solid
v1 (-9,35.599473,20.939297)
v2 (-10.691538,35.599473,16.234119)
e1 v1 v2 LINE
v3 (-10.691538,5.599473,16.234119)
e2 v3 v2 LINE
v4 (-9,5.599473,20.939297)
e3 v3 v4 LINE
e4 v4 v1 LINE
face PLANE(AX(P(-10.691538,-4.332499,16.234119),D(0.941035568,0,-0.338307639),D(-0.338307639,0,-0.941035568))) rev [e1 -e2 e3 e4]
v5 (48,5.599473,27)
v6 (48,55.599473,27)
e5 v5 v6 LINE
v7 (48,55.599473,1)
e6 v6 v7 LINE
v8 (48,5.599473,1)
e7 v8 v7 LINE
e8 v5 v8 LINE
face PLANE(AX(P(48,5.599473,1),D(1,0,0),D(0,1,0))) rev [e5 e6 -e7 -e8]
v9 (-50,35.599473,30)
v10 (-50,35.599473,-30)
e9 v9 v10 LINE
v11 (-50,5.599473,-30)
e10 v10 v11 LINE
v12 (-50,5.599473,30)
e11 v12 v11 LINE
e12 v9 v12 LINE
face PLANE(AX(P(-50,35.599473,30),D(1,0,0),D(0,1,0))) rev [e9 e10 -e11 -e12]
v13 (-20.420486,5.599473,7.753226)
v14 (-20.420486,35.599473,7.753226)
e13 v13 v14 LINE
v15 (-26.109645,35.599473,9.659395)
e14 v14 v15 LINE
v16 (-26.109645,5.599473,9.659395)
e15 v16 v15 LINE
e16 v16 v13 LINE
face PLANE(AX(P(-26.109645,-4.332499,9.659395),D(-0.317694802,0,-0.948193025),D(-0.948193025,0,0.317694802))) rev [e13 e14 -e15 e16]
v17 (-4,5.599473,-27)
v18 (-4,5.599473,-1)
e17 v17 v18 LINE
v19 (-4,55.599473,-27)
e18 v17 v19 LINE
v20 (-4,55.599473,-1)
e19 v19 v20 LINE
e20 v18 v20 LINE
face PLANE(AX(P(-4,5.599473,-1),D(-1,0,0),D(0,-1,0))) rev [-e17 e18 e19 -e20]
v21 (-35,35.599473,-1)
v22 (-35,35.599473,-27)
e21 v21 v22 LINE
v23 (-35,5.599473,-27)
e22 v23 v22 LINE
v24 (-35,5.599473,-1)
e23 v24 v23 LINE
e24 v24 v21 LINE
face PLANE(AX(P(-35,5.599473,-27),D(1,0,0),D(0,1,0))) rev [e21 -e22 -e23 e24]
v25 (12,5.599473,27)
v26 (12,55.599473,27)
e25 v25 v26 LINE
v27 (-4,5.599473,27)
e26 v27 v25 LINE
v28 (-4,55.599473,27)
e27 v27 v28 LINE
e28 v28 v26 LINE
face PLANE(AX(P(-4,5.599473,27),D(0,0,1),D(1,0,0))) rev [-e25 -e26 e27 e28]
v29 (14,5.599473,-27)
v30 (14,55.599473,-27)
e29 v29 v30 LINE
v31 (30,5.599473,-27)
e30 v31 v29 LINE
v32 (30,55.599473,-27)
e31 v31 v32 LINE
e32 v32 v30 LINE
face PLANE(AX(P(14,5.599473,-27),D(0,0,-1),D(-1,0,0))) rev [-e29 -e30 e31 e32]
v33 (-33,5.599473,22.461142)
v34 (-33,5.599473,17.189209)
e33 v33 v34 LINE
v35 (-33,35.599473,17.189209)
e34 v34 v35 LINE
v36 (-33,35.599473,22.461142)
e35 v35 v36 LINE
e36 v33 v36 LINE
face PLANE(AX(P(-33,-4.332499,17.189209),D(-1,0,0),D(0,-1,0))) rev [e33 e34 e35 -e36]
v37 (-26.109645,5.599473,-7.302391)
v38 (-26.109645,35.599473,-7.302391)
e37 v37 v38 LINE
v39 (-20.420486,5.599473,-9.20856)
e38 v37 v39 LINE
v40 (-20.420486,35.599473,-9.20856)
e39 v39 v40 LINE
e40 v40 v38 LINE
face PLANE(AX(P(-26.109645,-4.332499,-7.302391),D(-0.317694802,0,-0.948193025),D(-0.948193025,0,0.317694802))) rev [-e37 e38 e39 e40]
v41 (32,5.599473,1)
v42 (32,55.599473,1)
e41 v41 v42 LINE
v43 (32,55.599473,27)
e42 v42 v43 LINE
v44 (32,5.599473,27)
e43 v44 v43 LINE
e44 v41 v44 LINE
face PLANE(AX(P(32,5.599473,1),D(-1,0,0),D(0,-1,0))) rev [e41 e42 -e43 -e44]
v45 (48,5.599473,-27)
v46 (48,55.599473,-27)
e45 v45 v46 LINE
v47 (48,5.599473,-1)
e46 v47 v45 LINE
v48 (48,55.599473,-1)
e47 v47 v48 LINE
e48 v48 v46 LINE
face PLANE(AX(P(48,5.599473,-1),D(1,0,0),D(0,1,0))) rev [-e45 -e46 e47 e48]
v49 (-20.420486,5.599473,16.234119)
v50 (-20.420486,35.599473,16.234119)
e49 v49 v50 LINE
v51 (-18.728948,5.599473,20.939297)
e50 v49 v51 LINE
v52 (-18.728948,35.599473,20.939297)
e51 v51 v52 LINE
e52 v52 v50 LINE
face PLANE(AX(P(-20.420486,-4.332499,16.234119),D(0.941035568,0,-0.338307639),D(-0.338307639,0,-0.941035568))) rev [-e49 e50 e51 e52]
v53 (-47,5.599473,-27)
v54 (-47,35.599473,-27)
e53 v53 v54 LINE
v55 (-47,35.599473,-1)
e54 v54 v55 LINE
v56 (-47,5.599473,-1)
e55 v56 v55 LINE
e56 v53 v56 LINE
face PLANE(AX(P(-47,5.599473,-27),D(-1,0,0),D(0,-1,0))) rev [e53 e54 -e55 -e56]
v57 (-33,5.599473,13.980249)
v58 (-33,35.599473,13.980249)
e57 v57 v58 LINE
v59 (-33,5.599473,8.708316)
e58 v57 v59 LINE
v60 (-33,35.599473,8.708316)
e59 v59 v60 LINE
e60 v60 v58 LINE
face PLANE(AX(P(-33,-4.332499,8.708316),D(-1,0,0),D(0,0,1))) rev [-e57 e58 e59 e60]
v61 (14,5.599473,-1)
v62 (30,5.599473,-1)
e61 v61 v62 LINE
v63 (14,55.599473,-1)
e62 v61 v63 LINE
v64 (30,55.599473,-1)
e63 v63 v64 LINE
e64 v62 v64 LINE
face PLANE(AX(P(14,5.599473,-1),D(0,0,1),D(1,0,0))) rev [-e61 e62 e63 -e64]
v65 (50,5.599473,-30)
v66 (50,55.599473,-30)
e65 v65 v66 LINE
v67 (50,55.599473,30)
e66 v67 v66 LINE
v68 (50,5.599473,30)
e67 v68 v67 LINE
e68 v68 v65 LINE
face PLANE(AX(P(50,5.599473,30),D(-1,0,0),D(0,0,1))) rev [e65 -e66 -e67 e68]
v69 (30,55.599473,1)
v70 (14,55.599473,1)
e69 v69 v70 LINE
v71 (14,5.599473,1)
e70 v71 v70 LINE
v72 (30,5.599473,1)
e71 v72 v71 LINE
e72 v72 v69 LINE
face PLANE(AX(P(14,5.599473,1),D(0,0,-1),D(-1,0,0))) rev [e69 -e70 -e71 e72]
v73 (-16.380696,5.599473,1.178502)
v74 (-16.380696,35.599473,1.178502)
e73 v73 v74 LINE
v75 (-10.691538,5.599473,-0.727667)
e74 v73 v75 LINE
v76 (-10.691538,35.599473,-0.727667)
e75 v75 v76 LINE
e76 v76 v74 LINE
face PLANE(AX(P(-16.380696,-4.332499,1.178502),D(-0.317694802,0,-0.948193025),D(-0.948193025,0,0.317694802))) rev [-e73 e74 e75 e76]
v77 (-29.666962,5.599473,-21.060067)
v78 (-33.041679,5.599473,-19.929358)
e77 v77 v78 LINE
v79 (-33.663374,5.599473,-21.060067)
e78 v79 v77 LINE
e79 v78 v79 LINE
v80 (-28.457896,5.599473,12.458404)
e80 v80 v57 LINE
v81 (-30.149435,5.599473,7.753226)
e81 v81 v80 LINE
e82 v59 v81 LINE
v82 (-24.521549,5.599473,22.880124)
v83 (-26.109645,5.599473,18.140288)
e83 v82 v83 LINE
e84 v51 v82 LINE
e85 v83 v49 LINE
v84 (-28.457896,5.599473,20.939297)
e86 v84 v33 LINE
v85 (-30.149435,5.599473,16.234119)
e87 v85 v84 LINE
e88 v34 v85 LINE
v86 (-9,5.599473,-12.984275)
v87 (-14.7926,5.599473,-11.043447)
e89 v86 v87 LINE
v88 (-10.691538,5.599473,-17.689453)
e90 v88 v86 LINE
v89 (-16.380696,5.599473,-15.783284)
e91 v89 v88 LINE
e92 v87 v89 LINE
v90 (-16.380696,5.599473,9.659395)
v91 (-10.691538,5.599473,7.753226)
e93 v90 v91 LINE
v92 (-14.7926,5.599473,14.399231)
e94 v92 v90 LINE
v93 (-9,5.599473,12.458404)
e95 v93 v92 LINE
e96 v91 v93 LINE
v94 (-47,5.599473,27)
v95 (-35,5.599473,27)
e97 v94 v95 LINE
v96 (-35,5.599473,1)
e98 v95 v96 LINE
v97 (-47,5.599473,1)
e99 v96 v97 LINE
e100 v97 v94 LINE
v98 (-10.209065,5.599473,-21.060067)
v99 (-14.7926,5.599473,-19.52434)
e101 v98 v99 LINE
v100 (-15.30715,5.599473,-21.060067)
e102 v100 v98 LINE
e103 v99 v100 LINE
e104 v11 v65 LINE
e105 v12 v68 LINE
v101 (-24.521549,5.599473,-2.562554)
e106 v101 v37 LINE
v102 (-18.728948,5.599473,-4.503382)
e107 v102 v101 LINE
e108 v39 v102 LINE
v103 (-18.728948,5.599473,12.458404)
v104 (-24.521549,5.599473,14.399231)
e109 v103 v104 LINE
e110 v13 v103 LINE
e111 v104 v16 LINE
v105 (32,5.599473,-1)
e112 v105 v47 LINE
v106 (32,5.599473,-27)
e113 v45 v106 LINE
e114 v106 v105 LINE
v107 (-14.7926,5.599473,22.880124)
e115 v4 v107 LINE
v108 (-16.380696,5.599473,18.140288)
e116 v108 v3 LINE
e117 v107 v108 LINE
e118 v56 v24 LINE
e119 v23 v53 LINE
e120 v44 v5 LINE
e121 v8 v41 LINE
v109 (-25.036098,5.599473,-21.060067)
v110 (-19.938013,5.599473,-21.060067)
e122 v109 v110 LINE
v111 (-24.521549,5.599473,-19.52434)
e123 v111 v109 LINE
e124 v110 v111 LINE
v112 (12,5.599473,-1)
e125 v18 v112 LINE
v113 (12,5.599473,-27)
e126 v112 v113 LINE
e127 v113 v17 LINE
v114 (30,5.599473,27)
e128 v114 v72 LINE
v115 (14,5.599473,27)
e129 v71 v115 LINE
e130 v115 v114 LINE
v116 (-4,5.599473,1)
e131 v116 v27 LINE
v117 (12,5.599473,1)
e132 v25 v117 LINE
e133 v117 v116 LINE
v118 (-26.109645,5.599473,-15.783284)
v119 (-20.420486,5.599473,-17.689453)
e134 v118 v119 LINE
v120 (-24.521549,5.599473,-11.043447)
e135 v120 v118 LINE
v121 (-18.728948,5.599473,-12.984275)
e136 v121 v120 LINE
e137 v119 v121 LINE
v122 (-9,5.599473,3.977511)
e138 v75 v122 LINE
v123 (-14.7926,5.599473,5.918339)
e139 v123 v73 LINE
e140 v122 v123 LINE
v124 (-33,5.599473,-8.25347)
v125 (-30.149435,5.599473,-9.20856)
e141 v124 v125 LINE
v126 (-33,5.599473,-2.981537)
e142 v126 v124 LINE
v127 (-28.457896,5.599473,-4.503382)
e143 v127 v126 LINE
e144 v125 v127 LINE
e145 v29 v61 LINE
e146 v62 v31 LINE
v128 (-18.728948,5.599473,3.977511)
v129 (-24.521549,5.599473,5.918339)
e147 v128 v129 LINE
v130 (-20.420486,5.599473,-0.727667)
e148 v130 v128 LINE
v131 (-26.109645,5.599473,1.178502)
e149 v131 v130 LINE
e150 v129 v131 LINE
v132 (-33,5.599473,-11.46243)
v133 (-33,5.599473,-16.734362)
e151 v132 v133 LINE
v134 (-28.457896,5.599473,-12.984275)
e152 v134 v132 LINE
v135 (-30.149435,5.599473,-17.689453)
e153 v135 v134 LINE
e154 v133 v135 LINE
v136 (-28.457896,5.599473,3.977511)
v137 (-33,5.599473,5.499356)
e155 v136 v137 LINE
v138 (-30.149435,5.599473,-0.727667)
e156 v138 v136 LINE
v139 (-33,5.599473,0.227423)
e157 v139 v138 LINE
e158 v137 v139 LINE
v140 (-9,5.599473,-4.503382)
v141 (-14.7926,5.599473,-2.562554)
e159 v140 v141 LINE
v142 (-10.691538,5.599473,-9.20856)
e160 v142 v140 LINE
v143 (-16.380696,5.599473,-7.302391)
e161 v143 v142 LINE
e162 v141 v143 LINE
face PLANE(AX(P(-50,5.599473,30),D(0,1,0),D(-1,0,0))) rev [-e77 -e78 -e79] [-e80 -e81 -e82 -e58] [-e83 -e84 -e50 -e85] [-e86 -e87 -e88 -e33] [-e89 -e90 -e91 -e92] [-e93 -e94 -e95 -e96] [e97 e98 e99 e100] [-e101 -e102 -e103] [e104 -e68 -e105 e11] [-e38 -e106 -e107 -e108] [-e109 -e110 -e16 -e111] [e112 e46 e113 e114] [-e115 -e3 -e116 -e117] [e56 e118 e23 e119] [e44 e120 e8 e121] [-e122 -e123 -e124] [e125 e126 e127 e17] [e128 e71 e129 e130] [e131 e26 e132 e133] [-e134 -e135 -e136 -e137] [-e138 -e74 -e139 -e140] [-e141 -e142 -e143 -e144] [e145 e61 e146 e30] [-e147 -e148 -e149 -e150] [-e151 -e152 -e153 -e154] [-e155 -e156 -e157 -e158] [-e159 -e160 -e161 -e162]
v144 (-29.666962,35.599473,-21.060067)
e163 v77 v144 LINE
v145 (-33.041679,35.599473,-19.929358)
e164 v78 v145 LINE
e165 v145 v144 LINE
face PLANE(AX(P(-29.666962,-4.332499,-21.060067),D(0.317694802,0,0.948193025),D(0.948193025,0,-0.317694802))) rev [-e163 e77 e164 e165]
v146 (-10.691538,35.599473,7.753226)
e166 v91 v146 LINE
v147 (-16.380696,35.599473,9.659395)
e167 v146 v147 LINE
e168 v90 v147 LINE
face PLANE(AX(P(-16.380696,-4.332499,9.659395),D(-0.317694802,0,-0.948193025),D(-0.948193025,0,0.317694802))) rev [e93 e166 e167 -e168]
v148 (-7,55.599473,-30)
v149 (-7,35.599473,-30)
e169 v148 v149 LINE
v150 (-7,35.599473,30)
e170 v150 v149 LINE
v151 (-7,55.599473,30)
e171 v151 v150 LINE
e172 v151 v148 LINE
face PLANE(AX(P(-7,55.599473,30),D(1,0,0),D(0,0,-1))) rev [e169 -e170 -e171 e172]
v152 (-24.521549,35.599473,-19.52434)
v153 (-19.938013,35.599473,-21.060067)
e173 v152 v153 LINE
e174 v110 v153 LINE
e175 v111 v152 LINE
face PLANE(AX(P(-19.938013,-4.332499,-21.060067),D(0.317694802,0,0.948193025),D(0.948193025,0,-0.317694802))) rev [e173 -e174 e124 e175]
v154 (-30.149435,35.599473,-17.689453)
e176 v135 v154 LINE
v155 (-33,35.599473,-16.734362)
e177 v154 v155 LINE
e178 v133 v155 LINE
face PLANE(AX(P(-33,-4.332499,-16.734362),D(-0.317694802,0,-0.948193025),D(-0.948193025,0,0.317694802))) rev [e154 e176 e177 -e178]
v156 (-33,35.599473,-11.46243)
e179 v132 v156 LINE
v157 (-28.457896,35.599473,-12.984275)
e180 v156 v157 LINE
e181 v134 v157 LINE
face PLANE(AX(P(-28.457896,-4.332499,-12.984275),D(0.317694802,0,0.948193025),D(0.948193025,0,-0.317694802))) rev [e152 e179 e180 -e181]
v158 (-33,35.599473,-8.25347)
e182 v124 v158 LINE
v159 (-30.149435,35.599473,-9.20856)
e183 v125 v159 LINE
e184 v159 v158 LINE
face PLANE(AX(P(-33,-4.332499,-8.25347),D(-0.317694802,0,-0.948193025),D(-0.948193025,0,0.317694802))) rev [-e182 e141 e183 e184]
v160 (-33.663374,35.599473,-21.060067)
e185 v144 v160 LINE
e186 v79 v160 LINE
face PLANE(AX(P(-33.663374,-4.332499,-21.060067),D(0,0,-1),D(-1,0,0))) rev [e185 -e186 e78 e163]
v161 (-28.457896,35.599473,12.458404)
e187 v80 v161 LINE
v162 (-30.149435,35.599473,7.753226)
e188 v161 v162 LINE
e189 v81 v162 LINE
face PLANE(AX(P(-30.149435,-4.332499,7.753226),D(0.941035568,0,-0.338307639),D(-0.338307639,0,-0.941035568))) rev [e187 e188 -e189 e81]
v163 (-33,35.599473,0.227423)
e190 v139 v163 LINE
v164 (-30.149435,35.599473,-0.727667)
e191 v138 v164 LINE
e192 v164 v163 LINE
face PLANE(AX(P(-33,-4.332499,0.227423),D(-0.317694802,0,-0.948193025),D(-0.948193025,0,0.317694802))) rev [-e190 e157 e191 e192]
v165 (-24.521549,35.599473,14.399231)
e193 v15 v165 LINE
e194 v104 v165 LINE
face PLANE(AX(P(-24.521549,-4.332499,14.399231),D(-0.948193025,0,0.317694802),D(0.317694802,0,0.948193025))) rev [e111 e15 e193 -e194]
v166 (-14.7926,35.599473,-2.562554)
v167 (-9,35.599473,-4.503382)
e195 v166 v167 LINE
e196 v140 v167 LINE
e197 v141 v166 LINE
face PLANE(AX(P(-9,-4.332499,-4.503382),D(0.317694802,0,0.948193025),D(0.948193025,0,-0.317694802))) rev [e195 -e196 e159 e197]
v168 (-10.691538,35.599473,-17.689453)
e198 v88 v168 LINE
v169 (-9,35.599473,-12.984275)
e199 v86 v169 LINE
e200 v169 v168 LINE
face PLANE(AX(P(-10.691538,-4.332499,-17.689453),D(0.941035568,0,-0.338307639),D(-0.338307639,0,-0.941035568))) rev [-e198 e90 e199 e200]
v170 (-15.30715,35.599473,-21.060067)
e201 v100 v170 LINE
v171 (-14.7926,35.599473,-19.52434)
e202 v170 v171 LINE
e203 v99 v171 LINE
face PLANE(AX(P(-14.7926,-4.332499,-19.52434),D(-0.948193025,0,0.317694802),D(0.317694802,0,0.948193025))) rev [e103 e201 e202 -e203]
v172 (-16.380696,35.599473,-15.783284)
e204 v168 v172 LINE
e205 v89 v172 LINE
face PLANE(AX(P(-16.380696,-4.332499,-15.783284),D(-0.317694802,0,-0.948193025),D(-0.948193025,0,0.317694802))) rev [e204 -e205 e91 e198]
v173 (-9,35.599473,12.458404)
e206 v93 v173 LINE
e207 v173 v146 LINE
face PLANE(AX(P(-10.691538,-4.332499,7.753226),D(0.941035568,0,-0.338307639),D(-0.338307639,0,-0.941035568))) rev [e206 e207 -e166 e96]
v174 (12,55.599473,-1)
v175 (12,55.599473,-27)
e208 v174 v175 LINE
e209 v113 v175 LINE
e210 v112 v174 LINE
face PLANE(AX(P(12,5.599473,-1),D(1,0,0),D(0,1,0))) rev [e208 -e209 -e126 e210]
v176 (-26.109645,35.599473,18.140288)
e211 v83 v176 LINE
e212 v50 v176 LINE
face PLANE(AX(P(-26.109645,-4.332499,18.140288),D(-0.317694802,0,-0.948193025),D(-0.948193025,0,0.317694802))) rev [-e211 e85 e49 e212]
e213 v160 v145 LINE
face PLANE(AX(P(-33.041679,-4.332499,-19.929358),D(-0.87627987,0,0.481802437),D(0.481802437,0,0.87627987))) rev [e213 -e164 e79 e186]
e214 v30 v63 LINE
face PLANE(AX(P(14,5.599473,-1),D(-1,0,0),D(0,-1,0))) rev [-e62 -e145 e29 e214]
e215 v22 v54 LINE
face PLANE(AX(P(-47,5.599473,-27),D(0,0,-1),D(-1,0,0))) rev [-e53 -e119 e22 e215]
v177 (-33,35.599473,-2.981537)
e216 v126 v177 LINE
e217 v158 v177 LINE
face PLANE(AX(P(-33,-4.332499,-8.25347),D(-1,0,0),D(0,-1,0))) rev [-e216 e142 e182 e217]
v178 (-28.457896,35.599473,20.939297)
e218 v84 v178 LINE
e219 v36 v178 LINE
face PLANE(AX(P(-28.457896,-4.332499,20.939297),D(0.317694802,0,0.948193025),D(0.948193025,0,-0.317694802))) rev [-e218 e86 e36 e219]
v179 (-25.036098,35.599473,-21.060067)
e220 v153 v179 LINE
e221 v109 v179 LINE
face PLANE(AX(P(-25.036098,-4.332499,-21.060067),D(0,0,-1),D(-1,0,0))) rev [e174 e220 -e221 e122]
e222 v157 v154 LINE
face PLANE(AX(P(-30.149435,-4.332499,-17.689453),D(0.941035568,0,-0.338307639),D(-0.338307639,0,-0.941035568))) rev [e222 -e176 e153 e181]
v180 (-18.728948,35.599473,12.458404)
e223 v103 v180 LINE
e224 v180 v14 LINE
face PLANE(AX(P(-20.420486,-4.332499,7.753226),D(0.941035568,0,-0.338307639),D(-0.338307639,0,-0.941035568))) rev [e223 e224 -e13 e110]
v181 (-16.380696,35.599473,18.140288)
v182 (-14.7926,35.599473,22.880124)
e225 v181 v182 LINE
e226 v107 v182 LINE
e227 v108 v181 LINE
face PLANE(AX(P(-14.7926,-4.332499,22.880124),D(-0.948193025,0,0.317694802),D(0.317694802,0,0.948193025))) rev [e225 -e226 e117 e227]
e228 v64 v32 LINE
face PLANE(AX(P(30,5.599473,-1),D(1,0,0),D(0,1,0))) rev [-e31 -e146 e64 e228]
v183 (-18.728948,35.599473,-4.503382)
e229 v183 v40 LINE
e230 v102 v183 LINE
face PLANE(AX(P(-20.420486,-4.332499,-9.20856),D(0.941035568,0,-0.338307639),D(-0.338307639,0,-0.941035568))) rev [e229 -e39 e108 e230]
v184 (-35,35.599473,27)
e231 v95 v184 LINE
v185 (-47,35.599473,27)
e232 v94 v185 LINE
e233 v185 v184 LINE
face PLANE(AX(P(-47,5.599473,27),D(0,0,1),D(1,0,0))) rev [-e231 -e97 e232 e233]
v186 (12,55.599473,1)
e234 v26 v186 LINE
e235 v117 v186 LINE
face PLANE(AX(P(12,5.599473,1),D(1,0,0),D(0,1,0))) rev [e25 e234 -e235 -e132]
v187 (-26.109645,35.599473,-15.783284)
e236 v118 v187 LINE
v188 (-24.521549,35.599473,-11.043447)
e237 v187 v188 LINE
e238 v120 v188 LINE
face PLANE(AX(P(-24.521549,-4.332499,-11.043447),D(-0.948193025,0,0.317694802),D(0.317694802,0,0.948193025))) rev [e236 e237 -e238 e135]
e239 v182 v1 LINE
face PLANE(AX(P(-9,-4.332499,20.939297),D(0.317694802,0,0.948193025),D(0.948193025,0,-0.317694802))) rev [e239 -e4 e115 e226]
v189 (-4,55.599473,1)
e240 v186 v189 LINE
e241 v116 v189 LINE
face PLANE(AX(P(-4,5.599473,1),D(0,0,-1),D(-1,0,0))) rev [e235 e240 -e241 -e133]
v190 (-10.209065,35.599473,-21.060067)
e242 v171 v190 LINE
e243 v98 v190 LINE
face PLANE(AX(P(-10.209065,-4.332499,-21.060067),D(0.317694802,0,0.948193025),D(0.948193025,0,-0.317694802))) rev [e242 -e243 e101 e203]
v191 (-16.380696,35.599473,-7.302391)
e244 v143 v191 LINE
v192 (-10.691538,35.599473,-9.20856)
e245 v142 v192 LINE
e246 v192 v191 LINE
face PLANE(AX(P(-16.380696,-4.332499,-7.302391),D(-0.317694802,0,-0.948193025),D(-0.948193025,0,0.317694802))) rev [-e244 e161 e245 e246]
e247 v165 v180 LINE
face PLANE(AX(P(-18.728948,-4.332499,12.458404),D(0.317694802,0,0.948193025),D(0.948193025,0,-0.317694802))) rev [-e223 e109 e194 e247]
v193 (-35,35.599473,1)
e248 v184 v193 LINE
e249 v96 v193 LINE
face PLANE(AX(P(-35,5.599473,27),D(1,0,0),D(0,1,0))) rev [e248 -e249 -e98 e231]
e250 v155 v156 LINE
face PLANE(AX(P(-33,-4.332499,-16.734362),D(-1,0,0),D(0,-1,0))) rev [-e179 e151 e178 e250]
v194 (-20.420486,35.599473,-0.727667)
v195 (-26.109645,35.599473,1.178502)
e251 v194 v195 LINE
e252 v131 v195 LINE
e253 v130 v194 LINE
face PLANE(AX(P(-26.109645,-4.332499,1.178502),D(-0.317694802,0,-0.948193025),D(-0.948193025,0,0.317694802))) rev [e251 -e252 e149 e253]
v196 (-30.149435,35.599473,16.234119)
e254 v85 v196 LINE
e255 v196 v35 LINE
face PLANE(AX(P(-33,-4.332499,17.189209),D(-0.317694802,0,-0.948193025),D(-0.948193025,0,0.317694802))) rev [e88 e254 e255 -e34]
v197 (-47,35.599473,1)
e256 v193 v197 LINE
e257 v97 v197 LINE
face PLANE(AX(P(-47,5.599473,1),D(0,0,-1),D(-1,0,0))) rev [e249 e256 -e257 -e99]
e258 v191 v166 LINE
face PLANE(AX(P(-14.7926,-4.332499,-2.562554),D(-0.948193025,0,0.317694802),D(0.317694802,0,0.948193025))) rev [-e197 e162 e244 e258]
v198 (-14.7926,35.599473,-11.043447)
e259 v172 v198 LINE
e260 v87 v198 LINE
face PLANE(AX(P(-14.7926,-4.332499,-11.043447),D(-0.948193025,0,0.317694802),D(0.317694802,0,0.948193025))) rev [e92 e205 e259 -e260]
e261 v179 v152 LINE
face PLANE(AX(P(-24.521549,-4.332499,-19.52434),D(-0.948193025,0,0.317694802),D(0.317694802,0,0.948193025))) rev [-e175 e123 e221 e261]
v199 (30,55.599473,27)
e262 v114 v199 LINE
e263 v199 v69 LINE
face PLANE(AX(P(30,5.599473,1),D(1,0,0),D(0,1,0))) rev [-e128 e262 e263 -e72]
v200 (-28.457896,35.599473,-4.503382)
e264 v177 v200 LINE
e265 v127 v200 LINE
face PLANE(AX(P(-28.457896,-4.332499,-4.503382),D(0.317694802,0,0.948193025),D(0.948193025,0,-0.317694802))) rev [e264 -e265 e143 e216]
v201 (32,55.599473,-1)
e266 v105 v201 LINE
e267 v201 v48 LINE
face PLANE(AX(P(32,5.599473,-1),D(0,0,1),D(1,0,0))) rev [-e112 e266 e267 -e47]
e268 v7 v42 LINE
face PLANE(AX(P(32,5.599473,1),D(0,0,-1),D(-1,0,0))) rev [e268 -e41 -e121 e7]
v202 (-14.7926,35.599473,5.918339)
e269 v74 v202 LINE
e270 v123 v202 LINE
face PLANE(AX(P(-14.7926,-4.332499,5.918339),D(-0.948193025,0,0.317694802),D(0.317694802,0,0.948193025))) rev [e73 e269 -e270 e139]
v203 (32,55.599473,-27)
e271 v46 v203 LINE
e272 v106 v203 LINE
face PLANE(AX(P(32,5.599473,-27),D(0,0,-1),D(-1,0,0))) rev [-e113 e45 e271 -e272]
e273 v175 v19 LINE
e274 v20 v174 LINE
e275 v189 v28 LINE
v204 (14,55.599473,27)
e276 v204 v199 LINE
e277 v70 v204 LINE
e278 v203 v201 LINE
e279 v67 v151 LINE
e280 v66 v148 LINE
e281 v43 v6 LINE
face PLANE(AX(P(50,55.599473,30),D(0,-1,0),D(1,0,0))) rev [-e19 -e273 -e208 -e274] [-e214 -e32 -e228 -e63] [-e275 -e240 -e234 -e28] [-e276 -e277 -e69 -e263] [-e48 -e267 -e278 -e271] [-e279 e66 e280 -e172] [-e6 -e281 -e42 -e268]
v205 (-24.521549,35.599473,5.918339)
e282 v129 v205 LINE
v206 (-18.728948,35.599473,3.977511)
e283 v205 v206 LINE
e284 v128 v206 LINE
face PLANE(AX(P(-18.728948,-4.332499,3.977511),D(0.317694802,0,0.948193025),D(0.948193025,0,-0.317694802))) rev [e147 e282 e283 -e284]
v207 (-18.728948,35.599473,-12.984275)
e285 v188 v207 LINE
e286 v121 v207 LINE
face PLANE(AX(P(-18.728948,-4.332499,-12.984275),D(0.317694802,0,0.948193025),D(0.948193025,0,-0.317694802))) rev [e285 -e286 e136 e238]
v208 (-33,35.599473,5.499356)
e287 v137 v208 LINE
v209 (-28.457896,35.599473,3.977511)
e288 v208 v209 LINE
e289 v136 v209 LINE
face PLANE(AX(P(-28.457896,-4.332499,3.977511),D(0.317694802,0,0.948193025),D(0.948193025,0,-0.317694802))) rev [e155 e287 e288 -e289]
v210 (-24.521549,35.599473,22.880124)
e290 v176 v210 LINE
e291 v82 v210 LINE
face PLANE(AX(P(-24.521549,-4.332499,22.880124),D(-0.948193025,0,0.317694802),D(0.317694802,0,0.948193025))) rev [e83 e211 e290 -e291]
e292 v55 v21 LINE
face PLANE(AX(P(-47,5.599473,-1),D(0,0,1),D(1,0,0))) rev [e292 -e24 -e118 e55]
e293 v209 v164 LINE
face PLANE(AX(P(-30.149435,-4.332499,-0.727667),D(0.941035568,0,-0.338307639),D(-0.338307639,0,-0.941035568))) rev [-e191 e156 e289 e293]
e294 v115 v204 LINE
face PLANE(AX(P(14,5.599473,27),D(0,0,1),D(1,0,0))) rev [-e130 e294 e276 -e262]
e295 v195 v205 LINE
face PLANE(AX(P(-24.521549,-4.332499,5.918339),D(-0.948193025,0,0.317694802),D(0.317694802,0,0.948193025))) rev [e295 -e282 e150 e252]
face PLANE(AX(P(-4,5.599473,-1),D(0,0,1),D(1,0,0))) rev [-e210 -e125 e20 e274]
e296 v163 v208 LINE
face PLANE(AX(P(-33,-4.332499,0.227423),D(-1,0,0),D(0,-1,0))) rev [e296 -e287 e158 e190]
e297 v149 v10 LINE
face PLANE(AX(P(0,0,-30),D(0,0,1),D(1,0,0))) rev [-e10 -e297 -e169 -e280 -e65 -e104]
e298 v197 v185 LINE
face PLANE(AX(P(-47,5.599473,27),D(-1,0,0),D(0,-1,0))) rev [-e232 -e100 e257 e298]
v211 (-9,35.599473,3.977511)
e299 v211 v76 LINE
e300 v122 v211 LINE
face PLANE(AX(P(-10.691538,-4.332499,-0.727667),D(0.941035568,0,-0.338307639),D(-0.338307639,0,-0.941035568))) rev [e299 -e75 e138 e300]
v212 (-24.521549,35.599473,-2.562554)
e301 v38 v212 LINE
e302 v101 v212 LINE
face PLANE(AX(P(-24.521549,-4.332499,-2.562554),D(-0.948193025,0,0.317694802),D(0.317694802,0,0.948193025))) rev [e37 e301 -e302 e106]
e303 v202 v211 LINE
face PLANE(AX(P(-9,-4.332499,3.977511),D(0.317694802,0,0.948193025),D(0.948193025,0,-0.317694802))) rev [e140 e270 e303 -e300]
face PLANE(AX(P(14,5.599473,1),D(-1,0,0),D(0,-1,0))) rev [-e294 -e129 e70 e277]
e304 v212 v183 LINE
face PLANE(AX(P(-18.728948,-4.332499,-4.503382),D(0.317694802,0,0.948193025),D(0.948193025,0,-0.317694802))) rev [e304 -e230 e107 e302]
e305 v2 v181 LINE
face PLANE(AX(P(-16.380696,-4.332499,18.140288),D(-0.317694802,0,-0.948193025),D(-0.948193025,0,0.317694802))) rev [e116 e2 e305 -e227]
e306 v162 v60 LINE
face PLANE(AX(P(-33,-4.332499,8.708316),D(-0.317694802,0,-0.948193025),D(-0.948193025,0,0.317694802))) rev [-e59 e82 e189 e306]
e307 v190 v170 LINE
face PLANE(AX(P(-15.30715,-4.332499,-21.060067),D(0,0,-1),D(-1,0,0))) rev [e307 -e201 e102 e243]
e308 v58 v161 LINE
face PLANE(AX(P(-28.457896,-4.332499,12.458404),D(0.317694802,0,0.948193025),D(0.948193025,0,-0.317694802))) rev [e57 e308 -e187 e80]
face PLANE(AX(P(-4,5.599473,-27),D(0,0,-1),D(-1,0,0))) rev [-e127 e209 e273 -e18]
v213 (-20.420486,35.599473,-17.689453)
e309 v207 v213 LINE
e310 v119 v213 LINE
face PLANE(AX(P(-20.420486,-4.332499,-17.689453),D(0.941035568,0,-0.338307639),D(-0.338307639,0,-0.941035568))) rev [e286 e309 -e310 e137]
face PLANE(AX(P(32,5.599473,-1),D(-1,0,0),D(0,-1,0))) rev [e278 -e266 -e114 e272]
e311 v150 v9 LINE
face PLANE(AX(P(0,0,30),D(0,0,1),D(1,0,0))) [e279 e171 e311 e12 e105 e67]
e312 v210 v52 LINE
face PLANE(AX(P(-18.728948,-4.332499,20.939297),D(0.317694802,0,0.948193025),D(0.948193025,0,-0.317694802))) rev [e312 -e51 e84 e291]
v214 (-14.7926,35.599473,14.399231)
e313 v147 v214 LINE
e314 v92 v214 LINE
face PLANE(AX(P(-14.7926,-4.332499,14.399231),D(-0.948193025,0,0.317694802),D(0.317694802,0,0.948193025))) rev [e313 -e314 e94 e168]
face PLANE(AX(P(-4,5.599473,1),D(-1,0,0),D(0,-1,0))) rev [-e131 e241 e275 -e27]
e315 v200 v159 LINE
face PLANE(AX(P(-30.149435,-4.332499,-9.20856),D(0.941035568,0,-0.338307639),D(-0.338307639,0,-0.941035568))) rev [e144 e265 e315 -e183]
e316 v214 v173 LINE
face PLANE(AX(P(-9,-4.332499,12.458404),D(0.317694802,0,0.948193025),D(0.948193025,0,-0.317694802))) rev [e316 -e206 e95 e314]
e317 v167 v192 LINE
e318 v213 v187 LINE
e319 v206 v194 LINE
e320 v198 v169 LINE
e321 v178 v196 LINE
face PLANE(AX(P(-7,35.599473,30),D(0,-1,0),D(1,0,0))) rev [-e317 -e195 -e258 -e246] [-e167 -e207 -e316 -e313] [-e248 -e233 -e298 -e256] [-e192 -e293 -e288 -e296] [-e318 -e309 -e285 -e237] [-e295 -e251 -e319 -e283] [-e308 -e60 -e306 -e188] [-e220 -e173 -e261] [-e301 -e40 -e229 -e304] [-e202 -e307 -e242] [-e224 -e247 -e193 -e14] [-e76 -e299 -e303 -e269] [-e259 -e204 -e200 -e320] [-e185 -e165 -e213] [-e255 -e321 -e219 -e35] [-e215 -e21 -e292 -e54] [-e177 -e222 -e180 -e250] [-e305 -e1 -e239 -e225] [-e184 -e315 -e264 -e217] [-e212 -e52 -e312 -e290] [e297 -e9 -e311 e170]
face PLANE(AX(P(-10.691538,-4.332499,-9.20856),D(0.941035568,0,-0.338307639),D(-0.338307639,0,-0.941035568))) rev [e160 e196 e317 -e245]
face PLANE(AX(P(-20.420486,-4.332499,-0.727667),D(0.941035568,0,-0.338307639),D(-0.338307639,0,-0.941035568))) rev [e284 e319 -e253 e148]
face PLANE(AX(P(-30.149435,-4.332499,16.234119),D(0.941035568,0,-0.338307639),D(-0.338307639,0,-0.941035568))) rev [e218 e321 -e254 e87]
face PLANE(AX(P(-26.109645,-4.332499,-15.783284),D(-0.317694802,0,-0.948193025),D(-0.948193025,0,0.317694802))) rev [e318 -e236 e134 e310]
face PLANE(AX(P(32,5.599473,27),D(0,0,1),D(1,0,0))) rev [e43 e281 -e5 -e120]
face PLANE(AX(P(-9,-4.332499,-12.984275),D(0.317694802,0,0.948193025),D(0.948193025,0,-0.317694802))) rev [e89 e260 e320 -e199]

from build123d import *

# Parameters (mm, degrees)
STEPPED_BLOCK_DEPTH         = 30
LOWER_STEP_POCKETS_SKETCH_W = 16
LOWER_STEP_POCKETS_SKETCH_H = 26
LOWER_STEP_POCKETS_DEPTH    = 77.811457479
UPPER_STEP_POCKETS_SKETCH_W = 12
UPPER_STEP_POCKETS_SKETCH_H = 26
UPPER_STEP_POCKETS_DEPTH    = 66.574385243
TRIANGULAR_CUTS_DEPTH       = 30


with BuildPart() as part:
    # Stepped Block Profile → Stepped Block (new, symmetric)
    with BuildSketch(Plane.XY):
        Polygon((-50, 5.599472991), (50, 5.599472991), (50, 55.599472991), (-7, 55.599472991), (-7, 35.599472991), (-50, 35.599472991), align=None)
    extrude(amount=STEPPED_BLOCK_DEPTH, both=True)

    # Lower Step Pockets Sketch → Lower Step Pockets (cut, through all)
    with BuildSketch(Plane(origin=(0, 55.599472991, 0), x_dir=(1, 0, 0), z_dir=(0, 1, 0))):
        with Locations((4, -14)):
            Rectangle(LOWER_STEP_POCKETS_SKETCH_W, LOWER_STEP_POCKETS_SKETCH_H)
        with Locations((22, -14)):
            Rectangle(LOWER_STEP_POCKETS_SKETCH_W, LOWER_STEP_POCKETS_SKETCH_H)
        with Locations((40, -14)):
            Rectangle(LOWER_STEP_POCKETS_SKETCH_W, LOWER_STEP_POCKETS_SKETCH_H)
        with Locations((40, 14)):
            Rectangle(LOWER_STEP_POCKETS_SKETCH_W, LOWER_STEP_POCKETS_SKETCH_H)
        with Locations((22, 14)):
            Rectangle(LOWER_STEP_POCKETS_SKETCH_W, LOWER_STEP_POCKETS_SKETCH_H)
        with Locations((4, 14)):
            Rectangle(LOWER_STEP_POCKETS_SKETCH_W, LOWER_STEP_POCKETS_SKETCH_H)
    extrude(amount=-LOWER_STEP_POCKETS_DEPTH, mode=Mode.SUBTRACT)

    # Upper Step Pockets Sketch → Upper Step Pockets (cut, through all)
    with BuildSketch(Plane(origin=(0, 35.599472991, 0), x_dir=(1, 0, 0), z_dir=(0, 1, 0))):
        with Locations((-41, -14)):
            Rectangle(UPPER_STEP_POCKETS_SKETCH_W, UPPER_STEP_POCKETS_SKETCH_H)
        with Locations((-41, 14)):
            Rectangle(UPPER_STEP_POCKETS_SKETCH_W, UPPER_STEP_POCKETS_SKETCH_H)
    extrude(amount=-UPPER_STEP_POCKETS_DEPTH, mode=Mode.SUBTRACT)

    # Triangular Cuts Sketch → Triangular Cuts (cut)
    with BuildSketch(Plane(origin=(0, 35.599472991, 0), x_dir=(1, 0, 0), z_dir=(0, 1, 0))):
        Polygon((-33.663373821, 21.060066869), (-29.666961616, 21.060066869), (-33.0416794, 19.929357963), align=None)
        Polygon((-33, 16.73436244), (-33, 11.462429856), (-28.457896441, 12.984274726), (-30.149434639, 17.689452568), align=None)
        Polygon((-18.728948221, -20.939296913), (-24.521548709, -22.880124378), (-26.109644568, -18.140287882), (-20.420486418, -16.234119071), align=None)
        Polygon((-9, -20.939296913), (-14.792600489, -22.880124378), (-16.380696348, -18.140287882), (-10.691538197, -16.234119071), align=None)
        Polygon((-28.457896441, -20.939296913), (-33, -22.461141782), (-33, -17.189209199), (-30.149434639, -16.234119071), align=None)
        Polygon((-18.728948221, -12.458404003), (-24.521548709, -14.399231468), (-26.109644568, -9.659394973), (-20.420486418, -7.753226161), align=None)
        Polygon((-33, 8.25346953), (-33, 2.981536947), (-28.457896441, 4.503381816), (-30.149434639, 9.208559658), align=None)
        Polygon((-28.457896441, -12.458404003), (-33, -13.980248873), (-33, -8.708316289), (-30.149434639, -7.753226161), align=None)
        Polygon((-18.728948221, -3.977511094), (-24.521548709, -5.918338558), (-26.109644568, -1.178502063), (-20.420486418, 0.727666749), align=None)
        Polygon((-28.457896441, -3.977511094), (-33, -5.499355963), (-33, -0.22742338), (-30.149434639, 0.727666749), align=None)
        Polygon((-18.728948221, 4.503381816), (-24.521548709, 2.562554351), (-26.109644568, 7.302390847), (-20.420486418, 9.208559658), align=None)
        Polygon((-18.728948221, 12.984274726), (-24.521548709, 11.043447261), (-26.109644568, 15.783283756), (-20.420486418, 17.689452568), align=None)
        Polygon((-19.938013396, 21.060066869), (-24.521548709, 19.524340171), (-25.036098359, 21.060066869), align=None)
        Polygon((-9, -12.458404003), (-14.792600489, -14.399231468), (-16.380696348, -9.659394973), (-10.691538197, -7.753226161), align=None)
        Polygon((-9, -3.977511094), (-14.792600489, -5.918338558), (-16.380696348, -1.178502063), (-10.691538197, 0.727666749), align=None)
        Polygon((-9, 4.503381816), (-14.792600489, 2.562554351), (-16.380696348, 7.302390847), (-10.691538197, 9.208559658), align=None)
        Polygon((-9, 12.984274726), (-14.792600489, 11.043447261), (-16.380696348, 15.783283756), (-10.691538197, 17.689452568), align=None)
        Polygon((-10.209065175, 21.060066869), (-14.792600489, 19.524340171), (-15.307150139, 21.060066869), align=None)
    extrude(amount=-TRIANGULAR_CUTS_DEPTH, mode=Mode.SUBTRACT)


solid = part.part
